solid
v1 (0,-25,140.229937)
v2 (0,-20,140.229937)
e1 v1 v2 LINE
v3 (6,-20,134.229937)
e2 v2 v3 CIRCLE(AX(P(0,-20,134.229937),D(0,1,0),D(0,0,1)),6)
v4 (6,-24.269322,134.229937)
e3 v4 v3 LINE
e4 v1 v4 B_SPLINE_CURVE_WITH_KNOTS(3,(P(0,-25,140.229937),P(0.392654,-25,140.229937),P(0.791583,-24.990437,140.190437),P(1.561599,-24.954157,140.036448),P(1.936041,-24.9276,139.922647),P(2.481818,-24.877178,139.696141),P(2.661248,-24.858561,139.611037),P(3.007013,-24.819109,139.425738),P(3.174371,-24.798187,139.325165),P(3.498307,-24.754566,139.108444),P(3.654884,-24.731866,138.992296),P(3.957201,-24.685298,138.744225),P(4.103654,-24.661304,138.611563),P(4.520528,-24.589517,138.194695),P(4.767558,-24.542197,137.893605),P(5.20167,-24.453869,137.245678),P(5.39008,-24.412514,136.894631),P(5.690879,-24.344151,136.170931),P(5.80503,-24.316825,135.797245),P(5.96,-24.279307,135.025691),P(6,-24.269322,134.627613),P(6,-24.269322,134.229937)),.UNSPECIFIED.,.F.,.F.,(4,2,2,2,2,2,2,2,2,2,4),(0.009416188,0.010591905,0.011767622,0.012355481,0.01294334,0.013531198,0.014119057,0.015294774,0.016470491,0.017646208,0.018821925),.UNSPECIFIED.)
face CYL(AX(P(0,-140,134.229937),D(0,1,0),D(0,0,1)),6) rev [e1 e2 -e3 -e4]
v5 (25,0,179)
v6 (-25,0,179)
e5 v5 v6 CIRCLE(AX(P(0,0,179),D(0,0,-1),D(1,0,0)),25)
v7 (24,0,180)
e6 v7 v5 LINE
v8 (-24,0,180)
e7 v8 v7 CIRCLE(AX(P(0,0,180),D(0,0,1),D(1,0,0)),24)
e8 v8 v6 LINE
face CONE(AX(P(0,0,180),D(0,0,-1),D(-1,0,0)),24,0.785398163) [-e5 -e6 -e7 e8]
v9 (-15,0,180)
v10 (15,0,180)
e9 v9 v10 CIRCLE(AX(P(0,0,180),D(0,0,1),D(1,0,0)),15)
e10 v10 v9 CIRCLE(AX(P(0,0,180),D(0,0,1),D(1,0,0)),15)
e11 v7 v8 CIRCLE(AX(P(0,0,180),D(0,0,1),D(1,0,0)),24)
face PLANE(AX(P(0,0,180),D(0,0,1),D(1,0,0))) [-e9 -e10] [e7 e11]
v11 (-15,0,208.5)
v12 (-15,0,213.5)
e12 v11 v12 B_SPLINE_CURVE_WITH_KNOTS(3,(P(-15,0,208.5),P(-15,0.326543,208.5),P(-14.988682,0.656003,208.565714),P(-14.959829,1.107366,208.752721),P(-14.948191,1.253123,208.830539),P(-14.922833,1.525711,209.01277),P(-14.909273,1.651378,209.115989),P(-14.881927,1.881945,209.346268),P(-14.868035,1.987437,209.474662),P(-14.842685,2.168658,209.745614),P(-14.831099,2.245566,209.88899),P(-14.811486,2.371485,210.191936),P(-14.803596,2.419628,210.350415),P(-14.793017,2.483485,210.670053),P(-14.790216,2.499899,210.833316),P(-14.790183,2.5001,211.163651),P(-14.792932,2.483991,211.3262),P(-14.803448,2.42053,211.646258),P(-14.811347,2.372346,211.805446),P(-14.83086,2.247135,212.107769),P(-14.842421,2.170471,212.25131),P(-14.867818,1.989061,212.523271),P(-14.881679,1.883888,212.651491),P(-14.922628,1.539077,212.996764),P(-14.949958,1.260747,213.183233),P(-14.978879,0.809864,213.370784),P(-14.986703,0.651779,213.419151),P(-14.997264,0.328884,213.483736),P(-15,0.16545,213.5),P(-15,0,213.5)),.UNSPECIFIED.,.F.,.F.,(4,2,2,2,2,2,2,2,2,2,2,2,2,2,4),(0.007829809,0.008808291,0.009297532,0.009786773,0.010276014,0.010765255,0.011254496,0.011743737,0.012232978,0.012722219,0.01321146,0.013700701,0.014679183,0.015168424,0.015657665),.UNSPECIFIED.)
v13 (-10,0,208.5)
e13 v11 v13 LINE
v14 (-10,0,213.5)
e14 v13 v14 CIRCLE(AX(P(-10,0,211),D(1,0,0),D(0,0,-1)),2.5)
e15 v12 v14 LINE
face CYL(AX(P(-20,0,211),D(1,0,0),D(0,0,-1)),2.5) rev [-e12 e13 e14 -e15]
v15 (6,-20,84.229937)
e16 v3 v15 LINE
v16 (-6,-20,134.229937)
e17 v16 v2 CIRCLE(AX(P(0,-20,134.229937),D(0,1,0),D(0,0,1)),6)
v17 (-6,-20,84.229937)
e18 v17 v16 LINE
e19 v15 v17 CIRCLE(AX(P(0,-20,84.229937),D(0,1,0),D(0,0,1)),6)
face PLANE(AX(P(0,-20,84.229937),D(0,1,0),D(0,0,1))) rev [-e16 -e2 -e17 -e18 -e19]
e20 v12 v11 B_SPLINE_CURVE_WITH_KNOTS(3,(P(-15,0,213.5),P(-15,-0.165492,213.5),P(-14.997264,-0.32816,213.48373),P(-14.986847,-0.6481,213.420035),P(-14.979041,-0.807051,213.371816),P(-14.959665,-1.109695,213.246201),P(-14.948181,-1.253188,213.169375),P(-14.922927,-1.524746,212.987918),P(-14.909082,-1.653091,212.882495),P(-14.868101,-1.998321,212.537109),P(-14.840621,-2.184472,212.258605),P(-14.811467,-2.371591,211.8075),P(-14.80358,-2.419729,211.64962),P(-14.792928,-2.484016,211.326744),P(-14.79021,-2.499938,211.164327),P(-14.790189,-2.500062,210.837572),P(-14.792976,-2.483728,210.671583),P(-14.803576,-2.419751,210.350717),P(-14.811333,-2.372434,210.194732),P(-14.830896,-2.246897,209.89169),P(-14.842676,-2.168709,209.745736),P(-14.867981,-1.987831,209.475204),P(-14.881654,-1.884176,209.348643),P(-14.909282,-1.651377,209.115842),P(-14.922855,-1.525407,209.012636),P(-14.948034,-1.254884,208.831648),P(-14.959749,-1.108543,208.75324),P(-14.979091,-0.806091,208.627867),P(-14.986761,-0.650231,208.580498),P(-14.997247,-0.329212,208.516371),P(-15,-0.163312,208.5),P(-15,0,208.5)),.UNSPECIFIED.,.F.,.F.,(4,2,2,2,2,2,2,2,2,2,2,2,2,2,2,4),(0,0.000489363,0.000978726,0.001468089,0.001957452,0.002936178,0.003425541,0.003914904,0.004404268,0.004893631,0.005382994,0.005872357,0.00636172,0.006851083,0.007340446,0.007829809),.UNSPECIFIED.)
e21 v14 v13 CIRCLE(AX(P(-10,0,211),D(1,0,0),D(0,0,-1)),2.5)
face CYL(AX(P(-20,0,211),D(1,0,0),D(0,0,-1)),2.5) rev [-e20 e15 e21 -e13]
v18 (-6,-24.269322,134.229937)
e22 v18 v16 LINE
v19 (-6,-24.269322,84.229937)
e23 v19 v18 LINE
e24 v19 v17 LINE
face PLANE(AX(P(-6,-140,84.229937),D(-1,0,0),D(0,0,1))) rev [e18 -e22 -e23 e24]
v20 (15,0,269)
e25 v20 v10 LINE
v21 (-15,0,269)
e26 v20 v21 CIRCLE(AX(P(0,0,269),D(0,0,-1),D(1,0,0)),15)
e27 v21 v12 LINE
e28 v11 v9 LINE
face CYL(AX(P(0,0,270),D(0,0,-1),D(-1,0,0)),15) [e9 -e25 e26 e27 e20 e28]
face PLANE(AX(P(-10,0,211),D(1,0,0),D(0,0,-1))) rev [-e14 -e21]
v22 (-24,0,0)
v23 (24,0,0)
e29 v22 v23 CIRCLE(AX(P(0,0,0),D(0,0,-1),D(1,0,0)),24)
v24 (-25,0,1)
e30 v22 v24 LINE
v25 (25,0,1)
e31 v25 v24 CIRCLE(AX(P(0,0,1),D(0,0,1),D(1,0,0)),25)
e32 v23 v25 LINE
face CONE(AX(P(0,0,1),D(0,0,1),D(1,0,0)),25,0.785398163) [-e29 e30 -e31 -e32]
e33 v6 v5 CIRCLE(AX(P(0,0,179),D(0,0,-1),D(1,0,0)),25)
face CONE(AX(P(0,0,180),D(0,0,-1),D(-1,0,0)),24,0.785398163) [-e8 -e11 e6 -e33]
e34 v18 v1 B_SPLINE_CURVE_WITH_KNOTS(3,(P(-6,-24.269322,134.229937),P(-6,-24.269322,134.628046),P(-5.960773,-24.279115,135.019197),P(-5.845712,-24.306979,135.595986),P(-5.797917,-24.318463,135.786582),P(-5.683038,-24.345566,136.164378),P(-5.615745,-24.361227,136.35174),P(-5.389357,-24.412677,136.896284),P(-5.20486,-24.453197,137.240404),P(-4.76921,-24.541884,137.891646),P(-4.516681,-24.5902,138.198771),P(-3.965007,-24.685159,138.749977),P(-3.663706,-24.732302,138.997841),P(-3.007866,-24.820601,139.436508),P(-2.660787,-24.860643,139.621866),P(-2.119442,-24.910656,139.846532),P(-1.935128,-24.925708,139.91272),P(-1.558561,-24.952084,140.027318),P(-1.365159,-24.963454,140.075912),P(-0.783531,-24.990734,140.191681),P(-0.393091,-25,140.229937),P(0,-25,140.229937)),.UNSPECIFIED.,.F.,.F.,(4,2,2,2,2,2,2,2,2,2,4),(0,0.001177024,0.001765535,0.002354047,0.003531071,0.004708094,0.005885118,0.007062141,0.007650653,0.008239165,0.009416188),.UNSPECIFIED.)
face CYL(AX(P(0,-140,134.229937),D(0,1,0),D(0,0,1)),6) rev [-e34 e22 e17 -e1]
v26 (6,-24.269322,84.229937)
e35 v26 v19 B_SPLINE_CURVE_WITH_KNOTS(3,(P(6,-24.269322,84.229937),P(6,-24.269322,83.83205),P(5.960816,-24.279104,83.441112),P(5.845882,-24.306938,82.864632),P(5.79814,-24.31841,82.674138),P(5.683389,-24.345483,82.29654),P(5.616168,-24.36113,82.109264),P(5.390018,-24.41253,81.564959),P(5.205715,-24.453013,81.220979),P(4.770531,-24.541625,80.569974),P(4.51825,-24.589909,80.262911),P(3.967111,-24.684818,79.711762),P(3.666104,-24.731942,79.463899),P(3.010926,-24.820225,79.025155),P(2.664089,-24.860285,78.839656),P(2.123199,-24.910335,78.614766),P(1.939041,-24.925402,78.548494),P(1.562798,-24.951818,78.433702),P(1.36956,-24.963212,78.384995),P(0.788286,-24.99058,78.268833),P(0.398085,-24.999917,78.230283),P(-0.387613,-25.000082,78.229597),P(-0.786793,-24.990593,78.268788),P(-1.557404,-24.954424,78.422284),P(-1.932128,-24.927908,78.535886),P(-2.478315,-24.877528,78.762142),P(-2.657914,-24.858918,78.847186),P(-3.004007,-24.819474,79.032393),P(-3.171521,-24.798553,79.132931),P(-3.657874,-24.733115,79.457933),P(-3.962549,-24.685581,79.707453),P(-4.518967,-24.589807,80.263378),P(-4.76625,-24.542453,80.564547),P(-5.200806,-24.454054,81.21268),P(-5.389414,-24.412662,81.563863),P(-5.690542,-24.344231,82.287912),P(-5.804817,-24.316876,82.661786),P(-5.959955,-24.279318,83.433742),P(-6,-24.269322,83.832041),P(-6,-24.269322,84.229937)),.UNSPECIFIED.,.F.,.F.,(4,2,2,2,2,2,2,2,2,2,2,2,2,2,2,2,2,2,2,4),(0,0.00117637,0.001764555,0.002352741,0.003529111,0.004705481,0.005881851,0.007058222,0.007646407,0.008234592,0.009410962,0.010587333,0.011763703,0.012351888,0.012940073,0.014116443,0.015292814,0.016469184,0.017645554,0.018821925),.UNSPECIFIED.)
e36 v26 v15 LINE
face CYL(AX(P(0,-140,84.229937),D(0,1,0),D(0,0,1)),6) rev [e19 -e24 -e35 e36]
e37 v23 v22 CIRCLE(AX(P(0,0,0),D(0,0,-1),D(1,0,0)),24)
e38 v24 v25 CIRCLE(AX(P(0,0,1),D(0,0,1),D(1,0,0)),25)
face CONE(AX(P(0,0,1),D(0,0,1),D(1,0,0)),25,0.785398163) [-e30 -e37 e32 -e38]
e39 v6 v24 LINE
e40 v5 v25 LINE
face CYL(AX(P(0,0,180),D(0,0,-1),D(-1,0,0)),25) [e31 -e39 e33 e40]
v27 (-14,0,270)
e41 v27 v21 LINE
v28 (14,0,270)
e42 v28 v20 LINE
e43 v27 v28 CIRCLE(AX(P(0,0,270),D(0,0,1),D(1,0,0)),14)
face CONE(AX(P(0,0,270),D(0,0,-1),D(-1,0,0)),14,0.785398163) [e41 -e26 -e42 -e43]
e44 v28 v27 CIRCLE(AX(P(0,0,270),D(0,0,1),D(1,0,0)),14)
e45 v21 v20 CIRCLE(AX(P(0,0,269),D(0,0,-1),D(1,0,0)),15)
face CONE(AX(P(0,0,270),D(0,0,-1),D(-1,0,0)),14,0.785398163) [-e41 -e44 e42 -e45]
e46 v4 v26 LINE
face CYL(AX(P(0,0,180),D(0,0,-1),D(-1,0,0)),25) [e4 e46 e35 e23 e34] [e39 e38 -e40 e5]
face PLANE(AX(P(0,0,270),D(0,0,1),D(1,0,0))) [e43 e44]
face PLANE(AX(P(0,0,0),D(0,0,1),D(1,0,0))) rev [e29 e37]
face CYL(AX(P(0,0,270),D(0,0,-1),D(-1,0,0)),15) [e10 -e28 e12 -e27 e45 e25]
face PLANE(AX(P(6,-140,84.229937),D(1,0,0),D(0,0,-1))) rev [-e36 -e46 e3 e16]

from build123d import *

# Parameters (mm, degrees)
SKETCH1_R           = 25
BOSS_EXTRUDE1_DEPTH = 180
SKETCH2_R           = 15
BOSS_EXTRUDE2_DEPTH = 90
CUT_EXTRUDE1_START  = -20
CUT_EXTRUDE1_DEPTH  = 120
CHAMFER1_SIZE       = 1
CUT_EXTRUDE2_START  = -10
SKETCH4_R           = 2.5
CUT_EXTRUDE2_DEPTH  = 10


with BuildPart() as part:
    # Sketch1 → Boss-Extrude1 (new body)
    with BuildSketch(Plane.XY):
        with Locations(Location((0, 0, 0), (0, 0, 180))):
            Circle(SKETCH1_R)
    extrude(amount=BOSS_EXTRUDE1_DEPTH)

    # Sketch2 → Boss-Extrude2 (add)
    with BuildSketch(Plane.XY.offset(180)):
        with Locations(Location((0, 0, 0), (0, 0, 180))):
            Circle(SKETCH2_R)
    extrude(amount=BOSS_EXTRUDE2_DEPTH)

    # Sketch3 → Cut-Extrude1 (cut)
    with BuildSketch(Plane(origin=(0, 0, 0), x_dir=(1, 0, 0), z_dir=(0, 1, 0)).offset(CUT_EXTRUDE1_START)):
        with BuildLine():
            Line((6, -84.229937471), (6, -134.229937471))
            ThreePointArc((6, -134.229937471), (0, -140.229937471), (-6, -134.229937471))
            Line((-6, -134.229937471), (-6, -84.229937471))
            ThreePointArc((-6, -84.229937471), (0, -78.229937471), (6, -84.229937471))
        make_face()
    extrude(amount=-CUT_EXTRUDE1_DEPTH, mode=Mode.SUBTRACT)

    # Chamfer1
    chamfer1_edges = [part.edges().sort_by_distance(p)[0] for p in [
        (25, 0, 0),
        (25, 0, 180),
        (15, 0, 270),
    ]]
    chamfer(chamfer1_edges, length=CHAMFER1_SIZE)

    # Sketch4 → Cut-Extrude2 (cut)
    with BuildSketch(Plane(origin=(0, 0, 0), x_dir=(0, 0, -1), z_dir=(1, 0, 0)).offset(CUT_EXTRUDE2_START)):
        with Locations((-211, 0)):
            Circle(SKETCH4_R)
    extrude(amount=-CUT_EXTRUDE2_DEPTH, mode=Mode.SUBTRACT)


solid = part.part
